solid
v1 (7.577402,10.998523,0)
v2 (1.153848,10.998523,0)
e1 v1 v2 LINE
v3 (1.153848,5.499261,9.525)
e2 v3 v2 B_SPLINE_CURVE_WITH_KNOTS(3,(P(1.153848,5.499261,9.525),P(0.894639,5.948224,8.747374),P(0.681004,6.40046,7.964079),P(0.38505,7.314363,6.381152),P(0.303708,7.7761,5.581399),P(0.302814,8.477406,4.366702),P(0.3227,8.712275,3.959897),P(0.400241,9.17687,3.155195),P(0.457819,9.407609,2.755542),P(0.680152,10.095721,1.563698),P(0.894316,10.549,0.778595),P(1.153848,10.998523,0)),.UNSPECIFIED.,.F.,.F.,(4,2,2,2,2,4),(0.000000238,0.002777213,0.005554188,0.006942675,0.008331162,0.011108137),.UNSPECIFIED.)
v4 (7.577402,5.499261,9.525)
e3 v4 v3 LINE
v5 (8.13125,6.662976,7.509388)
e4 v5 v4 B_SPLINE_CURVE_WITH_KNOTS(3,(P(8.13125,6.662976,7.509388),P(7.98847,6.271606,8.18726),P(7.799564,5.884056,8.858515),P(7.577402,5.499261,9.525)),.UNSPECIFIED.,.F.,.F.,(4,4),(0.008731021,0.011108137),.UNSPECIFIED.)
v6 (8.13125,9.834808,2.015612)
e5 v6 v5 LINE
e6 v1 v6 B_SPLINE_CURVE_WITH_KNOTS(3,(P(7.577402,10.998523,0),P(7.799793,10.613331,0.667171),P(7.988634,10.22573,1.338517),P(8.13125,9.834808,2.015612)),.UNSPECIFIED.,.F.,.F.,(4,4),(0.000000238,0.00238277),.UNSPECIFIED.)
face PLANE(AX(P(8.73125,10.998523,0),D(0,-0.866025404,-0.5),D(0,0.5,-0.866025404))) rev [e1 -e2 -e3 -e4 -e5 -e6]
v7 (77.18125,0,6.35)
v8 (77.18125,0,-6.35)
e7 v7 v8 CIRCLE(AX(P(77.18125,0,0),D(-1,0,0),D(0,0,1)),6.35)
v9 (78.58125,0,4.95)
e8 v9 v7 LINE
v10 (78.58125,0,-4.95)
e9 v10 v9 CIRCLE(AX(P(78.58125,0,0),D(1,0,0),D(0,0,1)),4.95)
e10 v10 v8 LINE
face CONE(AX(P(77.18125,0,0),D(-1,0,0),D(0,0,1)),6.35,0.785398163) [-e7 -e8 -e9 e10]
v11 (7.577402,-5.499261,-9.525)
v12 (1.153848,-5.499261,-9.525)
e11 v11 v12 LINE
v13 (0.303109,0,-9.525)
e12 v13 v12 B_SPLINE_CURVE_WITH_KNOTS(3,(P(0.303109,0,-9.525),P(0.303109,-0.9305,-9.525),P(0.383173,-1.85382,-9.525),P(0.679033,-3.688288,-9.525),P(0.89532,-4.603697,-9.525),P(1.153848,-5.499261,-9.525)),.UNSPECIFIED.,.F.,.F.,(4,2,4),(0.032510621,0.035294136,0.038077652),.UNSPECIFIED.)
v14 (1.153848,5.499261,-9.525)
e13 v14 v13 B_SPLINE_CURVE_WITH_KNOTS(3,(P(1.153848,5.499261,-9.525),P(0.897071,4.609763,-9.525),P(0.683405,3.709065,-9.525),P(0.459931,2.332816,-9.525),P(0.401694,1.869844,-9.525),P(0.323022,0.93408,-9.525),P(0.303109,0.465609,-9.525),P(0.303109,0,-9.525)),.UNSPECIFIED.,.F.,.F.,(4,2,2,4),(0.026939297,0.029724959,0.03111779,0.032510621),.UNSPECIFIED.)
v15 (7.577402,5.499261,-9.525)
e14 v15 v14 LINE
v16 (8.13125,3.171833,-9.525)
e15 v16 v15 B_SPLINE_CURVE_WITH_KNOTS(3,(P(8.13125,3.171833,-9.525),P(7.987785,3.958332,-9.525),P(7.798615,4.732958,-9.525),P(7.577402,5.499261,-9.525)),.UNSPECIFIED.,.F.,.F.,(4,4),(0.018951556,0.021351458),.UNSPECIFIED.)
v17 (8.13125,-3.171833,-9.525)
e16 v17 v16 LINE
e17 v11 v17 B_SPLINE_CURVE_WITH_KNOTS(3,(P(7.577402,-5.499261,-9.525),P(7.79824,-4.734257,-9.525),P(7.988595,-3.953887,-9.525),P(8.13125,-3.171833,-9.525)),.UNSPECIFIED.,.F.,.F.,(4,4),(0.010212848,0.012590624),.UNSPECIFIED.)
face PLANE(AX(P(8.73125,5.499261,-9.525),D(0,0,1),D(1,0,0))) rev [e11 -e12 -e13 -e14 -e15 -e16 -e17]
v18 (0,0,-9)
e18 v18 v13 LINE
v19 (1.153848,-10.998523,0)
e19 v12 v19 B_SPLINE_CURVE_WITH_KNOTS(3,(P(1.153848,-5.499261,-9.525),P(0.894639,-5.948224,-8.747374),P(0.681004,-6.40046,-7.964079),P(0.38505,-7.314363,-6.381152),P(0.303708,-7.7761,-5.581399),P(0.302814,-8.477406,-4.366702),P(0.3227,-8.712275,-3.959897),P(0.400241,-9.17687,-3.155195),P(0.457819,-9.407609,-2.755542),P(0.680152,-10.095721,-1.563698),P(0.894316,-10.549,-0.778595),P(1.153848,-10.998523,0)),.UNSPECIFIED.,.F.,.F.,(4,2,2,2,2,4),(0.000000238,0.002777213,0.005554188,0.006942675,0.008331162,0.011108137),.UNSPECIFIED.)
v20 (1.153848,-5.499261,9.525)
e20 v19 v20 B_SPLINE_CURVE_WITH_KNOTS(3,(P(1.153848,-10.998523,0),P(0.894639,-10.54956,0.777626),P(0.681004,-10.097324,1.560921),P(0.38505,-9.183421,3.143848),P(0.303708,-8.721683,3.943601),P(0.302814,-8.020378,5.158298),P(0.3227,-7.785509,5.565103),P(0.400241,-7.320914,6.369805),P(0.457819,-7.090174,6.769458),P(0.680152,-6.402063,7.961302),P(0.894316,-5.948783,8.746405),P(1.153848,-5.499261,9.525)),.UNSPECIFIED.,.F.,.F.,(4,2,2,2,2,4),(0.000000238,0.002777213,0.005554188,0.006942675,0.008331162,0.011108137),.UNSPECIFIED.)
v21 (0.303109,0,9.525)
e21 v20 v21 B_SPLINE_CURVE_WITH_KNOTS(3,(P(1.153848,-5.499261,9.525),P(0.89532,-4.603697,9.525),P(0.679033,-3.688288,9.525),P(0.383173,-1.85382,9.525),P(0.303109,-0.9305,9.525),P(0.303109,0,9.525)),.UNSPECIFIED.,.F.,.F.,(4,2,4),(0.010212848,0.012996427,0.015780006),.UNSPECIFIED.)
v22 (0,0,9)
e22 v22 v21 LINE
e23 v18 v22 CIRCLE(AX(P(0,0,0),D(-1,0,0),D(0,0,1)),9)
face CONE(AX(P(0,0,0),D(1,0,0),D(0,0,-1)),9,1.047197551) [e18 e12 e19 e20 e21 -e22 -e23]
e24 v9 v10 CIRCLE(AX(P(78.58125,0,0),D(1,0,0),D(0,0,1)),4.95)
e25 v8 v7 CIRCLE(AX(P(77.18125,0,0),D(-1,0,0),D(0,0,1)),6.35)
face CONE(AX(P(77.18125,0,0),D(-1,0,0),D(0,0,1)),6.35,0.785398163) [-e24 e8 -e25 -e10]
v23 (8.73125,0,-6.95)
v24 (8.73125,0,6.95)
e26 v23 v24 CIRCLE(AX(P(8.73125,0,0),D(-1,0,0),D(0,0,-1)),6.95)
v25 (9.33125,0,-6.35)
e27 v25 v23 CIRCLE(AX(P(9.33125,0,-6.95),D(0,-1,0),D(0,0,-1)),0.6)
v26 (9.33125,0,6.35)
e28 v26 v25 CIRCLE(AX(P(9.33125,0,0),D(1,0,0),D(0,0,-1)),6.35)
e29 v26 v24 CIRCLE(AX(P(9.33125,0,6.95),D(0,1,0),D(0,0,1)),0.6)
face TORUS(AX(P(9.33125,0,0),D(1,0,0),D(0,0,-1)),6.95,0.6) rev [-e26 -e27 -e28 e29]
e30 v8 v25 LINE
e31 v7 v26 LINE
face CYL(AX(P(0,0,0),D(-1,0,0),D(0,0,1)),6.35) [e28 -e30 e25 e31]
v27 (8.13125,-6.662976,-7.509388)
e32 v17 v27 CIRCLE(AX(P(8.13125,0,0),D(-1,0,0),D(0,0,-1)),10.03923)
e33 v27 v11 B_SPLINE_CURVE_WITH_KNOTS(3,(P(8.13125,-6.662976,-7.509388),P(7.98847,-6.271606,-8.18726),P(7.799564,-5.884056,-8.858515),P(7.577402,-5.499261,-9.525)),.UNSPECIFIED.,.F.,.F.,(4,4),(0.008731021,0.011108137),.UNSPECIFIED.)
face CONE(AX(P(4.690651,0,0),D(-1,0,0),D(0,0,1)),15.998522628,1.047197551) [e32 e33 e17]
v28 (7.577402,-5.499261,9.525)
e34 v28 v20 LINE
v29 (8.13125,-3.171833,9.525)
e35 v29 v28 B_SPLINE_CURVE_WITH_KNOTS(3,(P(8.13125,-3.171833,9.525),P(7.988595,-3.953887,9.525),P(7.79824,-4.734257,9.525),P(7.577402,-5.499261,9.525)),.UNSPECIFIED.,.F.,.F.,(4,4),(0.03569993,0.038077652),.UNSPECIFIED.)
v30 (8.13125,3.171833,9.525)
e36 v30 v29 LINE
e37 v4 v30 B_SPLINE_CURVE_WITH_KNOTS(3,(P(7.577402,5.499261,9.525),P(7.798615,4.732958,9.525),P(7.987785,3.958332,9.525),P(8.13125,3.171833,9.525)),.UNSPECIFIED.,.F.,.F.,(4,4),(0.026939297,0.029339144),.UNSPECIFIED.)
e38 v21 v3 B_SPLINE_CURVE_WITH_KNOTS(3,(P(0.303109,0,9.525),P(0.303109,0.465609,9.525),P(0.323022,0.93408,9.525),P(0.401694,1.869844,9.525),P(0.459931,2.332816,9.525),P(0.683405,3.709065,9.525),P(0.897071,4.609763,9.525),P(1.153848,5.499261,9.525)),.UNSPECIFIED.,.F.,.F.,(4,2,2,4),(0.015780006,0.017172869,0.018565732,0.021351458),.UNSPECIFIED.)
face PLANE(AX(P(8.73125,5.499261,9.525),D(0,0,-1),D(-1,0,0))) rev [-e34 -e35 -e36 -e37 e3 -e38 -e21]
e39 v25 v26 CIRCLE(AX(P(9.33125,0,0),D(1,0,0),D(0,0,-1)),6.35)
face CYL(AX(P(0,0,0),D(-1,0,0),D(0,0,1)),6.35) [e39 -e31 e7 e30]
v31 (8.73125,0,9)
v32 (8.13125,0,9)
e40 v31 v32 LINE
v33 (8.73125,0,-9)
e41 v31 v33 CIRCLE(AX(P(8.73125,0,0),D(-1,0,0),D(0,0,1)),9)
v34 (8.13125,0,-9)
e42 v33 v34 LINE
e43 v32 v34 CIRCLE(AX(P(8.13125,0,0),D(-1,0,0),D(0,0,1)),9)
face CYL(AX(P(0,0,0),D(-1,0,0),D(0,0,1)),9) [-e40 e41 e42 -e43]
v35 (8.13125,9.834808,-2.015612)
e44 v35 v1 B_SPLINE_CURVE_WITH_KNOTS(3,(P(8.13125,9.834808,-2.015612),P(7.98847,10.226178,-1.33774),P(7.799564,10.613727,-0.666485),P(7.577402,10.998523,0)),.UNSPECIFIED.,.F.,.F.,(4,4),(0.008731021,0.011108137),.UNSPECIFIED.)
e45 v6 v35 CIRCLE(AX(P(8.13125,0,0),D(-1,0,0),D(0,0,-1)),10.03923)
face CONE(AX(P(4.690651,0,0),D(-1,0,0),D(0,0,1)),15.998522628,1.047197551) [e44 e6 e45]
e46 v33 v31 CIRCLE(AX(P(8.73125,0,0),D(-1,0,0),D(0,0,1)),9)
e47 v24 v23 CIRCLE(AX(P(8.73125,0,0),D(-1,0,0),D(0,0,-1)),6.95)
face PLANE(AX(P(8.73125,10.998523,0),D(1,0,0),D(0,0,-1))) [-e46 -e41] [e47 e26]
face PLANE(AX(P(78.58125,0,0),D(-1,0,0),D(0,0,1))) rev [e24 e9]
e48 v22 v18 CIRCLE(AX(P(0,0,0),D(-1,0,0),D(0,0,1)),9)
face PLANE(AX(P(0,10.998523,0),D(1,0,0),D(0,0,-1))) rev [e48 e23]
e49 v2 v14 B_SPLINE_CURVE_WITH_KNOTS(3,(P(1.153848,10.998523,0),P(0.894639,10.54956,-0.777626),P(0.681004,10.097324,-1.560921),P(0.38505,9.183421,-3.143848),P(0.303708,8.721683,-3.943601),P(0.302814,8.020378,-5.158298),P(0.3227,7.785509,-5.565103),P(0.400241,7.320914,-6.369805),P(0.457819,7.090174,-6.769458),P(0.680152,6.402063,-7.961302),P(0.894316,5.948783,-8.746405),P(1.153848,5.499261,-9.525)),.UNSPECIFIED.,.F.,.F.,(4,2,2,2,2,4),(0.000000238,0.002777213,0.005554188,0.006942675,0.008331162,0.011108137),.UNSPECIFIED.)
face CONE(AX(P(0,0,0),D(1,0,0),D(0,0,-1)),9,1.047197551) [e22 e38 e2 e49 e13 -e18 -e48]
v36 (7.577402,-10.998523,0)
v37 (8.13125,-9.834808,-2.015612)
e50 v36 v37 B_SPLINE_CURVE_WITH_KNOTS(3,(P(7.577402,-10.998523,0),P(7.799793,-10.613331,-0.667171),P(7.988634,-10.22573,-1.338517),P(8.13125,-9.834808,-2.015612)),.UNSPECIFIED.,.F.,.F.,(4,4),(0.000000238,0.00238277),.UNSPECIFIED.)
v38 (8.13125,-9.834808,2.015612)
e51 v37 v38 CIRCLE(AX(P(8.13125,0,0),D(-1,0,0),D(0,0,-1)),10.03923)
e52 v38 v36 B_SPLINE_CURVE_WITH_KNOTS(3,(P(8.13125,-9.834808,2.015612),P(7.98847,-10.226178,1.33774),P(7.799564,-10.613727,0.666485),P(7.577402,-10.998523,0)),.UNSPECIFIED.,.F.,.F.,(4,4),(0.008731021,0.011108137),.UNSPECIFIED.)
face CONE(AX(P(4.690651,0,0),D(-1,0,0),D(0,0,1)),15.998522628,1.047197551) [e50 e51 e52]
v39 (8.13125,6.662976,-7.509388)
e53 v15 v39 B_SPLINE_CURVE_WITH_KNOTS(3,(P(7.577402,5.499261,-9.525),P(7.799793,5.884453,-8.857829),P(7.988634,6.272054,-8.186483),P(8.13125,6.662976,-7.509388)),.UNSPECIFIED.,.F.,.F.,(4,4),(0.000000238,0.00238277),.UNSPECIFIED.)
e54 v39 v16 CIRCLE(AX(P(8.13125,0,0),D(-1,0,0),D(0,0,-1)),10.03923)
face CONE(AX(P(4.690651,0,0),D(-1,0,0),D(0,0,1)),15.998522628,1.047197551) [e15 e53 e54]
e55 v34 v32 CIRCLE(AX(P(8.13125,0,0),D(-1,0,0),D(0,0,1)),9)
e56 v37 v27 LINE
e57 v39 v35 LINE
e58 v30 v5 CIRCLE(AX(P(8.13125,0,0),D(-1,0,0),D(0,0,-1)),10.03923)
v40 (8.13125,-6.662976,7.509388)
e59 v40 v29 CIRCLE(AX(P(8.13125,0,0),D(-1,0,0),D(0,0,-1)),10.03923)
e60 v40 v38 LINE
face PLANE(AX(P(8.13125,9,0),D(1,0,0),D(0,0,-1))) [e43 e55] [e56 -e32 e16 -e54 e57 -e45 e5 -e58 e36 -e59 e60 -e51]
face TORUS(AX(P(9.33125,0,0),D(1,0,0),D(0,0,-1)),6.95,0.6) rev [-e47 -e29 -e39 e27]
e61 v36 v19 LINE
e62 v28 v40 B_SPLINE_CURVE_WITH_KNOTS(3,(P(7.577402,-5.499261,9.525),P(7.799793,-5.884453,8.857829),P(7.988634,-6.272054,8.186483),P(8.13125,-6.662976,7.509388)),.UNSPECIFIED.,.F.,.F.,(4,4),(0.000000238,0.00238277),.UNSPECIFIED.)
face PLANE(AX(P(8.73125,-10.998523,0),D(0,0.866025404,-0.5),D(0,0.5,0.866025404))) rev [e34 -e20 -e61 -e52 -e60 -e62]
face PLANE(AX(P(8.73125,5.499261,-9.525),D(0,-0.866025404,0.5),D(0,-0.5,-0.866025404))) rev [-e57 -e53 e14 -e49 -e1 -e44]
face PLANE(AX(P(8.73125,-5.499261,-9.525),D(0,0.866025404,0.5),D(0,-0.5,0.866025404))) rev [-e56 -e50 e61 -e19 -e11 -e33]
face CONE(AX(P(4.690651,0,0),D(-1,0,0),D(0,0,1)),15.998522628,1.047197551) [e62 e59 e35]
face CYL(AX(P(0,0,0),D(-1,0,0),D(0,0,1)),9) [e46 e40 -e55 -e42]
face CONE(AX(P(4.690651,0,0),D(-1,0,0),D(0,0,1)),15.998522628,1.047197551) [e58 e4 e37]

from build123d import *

# Parameters (mm, degrees)
BASE_EXTRUDE_DEPTH = 8.73125
SKETCH4_W          = 0.6
SKETCH4_H          = 11.998522628
CHAMFER_2_SIZE     = 1.4
FILLET_2_R         = 0.6


with BuildPart() as part:
    # Sketch1 → Base-Extrude (new body)
    with BuildSketch(Plane(origin=(0, 0, 0), x_dir=(0, 0, -1), z_dir=(1, 0, 0))):
        Polygon((9.525, 5.499261314), (9.525, -5.499261314), (0, -10.998522628), (-9.525, -5.499261314), (-9.525, 5.499261314), (0, 10.998522628), align=None)
    extrude(amount=BASE_EXTRUDE_DEPTH)

    # Sketch2 → Boss-Revolve1 (revolve)
    with BuildSketch(Plane.XY, mode=Mode.PRIVATE) as boss_revolve1_sk:
        Polygon((0, 0), (78.58125, 0), (78.58125, 5.55625), (78.58125, 6.35), (27.8072, 6.35), (0, 6.35), align=None)
    revolve(boss_revolve1_sk.sketch.rotate(Axis((0, 0, 0), (1, 0, 0)), 90), axis=Axis((0, 0, 0), (1, 0, 0)))

    # Sketch3 → Cut-Revolve1 (revolve, cut)
    with BuildSketch(Plane.XY, mode=Mode.PRIVATE) as cut_revolve1_sk:
        Polygon((0, 9), (4.040598923, 15.998522628), (4.040598923, 20.998522628), (-10, 20.998522628), (-10, 9), align=None)
    revolve(cut_revolve1_sk.sketch.rotate(Axis((0, 0, 0), (1, 0, 0)), 300.000000006), axis=Axis((0, 0, 0), (1, 0, 0)), mode=Mode.SUBTRACT)

    # Sketch5 → Cut-Revolve2 (revolve, cut)
    with BuildSketch(Plane.XY, mode=Mode.PRIVATE) as cut_revolve2_sk:
        Polygon((8.73125, 9), (4.690651077, 15.998522628), (4.690651077, 20.998522628), (14.690651077, 20.998522628), (14.690651077, 9), align=None)
    revolve(cut_revolve2_sk.sketch.rotate(Axis((0, 0, 0), (1, 0, 0)), 90), axis=Axis((0, 0, 0), (1, 0, 0)), mode=Mode.SUBTRACT)

    # Sketch4 → Cut-Revolve3 (revolve, cut)
    with BuildSketch(Plane.XY, mode=Mode.PRIVATE) as cut_revolve3_sk:
        with Locations((8.43125, 14.999261314)):
            Rectangle(SKETCH4_W, SKETCH4_H)
    revolve(cut_revolve3_sk.sketch.rotate(Axis((0, 0, 0), (1, 0, 0)), 90), axis=Axis((0, 0, 0), (1, 0, 0)), mode=Mode.SUBTRACT)

    # Chamfer 2
    chamfer_2_edges = [part.edges().sort_by_distance(p)[0] for p in [
        (78.58125, 0, -6.35),
    ]]
    chamfer(chamfer_2_edges, length=CHAMFER_2_SIZE)

    # Fillet 2
    fillet_2_edges = [part.edges().sort_by_distance(p)[0] for p in [
        (8.73125, 0, -6.35),
    ]]
    fillet(fillet_2_edges, radius=FILLET_2_R)


solid = part.part
